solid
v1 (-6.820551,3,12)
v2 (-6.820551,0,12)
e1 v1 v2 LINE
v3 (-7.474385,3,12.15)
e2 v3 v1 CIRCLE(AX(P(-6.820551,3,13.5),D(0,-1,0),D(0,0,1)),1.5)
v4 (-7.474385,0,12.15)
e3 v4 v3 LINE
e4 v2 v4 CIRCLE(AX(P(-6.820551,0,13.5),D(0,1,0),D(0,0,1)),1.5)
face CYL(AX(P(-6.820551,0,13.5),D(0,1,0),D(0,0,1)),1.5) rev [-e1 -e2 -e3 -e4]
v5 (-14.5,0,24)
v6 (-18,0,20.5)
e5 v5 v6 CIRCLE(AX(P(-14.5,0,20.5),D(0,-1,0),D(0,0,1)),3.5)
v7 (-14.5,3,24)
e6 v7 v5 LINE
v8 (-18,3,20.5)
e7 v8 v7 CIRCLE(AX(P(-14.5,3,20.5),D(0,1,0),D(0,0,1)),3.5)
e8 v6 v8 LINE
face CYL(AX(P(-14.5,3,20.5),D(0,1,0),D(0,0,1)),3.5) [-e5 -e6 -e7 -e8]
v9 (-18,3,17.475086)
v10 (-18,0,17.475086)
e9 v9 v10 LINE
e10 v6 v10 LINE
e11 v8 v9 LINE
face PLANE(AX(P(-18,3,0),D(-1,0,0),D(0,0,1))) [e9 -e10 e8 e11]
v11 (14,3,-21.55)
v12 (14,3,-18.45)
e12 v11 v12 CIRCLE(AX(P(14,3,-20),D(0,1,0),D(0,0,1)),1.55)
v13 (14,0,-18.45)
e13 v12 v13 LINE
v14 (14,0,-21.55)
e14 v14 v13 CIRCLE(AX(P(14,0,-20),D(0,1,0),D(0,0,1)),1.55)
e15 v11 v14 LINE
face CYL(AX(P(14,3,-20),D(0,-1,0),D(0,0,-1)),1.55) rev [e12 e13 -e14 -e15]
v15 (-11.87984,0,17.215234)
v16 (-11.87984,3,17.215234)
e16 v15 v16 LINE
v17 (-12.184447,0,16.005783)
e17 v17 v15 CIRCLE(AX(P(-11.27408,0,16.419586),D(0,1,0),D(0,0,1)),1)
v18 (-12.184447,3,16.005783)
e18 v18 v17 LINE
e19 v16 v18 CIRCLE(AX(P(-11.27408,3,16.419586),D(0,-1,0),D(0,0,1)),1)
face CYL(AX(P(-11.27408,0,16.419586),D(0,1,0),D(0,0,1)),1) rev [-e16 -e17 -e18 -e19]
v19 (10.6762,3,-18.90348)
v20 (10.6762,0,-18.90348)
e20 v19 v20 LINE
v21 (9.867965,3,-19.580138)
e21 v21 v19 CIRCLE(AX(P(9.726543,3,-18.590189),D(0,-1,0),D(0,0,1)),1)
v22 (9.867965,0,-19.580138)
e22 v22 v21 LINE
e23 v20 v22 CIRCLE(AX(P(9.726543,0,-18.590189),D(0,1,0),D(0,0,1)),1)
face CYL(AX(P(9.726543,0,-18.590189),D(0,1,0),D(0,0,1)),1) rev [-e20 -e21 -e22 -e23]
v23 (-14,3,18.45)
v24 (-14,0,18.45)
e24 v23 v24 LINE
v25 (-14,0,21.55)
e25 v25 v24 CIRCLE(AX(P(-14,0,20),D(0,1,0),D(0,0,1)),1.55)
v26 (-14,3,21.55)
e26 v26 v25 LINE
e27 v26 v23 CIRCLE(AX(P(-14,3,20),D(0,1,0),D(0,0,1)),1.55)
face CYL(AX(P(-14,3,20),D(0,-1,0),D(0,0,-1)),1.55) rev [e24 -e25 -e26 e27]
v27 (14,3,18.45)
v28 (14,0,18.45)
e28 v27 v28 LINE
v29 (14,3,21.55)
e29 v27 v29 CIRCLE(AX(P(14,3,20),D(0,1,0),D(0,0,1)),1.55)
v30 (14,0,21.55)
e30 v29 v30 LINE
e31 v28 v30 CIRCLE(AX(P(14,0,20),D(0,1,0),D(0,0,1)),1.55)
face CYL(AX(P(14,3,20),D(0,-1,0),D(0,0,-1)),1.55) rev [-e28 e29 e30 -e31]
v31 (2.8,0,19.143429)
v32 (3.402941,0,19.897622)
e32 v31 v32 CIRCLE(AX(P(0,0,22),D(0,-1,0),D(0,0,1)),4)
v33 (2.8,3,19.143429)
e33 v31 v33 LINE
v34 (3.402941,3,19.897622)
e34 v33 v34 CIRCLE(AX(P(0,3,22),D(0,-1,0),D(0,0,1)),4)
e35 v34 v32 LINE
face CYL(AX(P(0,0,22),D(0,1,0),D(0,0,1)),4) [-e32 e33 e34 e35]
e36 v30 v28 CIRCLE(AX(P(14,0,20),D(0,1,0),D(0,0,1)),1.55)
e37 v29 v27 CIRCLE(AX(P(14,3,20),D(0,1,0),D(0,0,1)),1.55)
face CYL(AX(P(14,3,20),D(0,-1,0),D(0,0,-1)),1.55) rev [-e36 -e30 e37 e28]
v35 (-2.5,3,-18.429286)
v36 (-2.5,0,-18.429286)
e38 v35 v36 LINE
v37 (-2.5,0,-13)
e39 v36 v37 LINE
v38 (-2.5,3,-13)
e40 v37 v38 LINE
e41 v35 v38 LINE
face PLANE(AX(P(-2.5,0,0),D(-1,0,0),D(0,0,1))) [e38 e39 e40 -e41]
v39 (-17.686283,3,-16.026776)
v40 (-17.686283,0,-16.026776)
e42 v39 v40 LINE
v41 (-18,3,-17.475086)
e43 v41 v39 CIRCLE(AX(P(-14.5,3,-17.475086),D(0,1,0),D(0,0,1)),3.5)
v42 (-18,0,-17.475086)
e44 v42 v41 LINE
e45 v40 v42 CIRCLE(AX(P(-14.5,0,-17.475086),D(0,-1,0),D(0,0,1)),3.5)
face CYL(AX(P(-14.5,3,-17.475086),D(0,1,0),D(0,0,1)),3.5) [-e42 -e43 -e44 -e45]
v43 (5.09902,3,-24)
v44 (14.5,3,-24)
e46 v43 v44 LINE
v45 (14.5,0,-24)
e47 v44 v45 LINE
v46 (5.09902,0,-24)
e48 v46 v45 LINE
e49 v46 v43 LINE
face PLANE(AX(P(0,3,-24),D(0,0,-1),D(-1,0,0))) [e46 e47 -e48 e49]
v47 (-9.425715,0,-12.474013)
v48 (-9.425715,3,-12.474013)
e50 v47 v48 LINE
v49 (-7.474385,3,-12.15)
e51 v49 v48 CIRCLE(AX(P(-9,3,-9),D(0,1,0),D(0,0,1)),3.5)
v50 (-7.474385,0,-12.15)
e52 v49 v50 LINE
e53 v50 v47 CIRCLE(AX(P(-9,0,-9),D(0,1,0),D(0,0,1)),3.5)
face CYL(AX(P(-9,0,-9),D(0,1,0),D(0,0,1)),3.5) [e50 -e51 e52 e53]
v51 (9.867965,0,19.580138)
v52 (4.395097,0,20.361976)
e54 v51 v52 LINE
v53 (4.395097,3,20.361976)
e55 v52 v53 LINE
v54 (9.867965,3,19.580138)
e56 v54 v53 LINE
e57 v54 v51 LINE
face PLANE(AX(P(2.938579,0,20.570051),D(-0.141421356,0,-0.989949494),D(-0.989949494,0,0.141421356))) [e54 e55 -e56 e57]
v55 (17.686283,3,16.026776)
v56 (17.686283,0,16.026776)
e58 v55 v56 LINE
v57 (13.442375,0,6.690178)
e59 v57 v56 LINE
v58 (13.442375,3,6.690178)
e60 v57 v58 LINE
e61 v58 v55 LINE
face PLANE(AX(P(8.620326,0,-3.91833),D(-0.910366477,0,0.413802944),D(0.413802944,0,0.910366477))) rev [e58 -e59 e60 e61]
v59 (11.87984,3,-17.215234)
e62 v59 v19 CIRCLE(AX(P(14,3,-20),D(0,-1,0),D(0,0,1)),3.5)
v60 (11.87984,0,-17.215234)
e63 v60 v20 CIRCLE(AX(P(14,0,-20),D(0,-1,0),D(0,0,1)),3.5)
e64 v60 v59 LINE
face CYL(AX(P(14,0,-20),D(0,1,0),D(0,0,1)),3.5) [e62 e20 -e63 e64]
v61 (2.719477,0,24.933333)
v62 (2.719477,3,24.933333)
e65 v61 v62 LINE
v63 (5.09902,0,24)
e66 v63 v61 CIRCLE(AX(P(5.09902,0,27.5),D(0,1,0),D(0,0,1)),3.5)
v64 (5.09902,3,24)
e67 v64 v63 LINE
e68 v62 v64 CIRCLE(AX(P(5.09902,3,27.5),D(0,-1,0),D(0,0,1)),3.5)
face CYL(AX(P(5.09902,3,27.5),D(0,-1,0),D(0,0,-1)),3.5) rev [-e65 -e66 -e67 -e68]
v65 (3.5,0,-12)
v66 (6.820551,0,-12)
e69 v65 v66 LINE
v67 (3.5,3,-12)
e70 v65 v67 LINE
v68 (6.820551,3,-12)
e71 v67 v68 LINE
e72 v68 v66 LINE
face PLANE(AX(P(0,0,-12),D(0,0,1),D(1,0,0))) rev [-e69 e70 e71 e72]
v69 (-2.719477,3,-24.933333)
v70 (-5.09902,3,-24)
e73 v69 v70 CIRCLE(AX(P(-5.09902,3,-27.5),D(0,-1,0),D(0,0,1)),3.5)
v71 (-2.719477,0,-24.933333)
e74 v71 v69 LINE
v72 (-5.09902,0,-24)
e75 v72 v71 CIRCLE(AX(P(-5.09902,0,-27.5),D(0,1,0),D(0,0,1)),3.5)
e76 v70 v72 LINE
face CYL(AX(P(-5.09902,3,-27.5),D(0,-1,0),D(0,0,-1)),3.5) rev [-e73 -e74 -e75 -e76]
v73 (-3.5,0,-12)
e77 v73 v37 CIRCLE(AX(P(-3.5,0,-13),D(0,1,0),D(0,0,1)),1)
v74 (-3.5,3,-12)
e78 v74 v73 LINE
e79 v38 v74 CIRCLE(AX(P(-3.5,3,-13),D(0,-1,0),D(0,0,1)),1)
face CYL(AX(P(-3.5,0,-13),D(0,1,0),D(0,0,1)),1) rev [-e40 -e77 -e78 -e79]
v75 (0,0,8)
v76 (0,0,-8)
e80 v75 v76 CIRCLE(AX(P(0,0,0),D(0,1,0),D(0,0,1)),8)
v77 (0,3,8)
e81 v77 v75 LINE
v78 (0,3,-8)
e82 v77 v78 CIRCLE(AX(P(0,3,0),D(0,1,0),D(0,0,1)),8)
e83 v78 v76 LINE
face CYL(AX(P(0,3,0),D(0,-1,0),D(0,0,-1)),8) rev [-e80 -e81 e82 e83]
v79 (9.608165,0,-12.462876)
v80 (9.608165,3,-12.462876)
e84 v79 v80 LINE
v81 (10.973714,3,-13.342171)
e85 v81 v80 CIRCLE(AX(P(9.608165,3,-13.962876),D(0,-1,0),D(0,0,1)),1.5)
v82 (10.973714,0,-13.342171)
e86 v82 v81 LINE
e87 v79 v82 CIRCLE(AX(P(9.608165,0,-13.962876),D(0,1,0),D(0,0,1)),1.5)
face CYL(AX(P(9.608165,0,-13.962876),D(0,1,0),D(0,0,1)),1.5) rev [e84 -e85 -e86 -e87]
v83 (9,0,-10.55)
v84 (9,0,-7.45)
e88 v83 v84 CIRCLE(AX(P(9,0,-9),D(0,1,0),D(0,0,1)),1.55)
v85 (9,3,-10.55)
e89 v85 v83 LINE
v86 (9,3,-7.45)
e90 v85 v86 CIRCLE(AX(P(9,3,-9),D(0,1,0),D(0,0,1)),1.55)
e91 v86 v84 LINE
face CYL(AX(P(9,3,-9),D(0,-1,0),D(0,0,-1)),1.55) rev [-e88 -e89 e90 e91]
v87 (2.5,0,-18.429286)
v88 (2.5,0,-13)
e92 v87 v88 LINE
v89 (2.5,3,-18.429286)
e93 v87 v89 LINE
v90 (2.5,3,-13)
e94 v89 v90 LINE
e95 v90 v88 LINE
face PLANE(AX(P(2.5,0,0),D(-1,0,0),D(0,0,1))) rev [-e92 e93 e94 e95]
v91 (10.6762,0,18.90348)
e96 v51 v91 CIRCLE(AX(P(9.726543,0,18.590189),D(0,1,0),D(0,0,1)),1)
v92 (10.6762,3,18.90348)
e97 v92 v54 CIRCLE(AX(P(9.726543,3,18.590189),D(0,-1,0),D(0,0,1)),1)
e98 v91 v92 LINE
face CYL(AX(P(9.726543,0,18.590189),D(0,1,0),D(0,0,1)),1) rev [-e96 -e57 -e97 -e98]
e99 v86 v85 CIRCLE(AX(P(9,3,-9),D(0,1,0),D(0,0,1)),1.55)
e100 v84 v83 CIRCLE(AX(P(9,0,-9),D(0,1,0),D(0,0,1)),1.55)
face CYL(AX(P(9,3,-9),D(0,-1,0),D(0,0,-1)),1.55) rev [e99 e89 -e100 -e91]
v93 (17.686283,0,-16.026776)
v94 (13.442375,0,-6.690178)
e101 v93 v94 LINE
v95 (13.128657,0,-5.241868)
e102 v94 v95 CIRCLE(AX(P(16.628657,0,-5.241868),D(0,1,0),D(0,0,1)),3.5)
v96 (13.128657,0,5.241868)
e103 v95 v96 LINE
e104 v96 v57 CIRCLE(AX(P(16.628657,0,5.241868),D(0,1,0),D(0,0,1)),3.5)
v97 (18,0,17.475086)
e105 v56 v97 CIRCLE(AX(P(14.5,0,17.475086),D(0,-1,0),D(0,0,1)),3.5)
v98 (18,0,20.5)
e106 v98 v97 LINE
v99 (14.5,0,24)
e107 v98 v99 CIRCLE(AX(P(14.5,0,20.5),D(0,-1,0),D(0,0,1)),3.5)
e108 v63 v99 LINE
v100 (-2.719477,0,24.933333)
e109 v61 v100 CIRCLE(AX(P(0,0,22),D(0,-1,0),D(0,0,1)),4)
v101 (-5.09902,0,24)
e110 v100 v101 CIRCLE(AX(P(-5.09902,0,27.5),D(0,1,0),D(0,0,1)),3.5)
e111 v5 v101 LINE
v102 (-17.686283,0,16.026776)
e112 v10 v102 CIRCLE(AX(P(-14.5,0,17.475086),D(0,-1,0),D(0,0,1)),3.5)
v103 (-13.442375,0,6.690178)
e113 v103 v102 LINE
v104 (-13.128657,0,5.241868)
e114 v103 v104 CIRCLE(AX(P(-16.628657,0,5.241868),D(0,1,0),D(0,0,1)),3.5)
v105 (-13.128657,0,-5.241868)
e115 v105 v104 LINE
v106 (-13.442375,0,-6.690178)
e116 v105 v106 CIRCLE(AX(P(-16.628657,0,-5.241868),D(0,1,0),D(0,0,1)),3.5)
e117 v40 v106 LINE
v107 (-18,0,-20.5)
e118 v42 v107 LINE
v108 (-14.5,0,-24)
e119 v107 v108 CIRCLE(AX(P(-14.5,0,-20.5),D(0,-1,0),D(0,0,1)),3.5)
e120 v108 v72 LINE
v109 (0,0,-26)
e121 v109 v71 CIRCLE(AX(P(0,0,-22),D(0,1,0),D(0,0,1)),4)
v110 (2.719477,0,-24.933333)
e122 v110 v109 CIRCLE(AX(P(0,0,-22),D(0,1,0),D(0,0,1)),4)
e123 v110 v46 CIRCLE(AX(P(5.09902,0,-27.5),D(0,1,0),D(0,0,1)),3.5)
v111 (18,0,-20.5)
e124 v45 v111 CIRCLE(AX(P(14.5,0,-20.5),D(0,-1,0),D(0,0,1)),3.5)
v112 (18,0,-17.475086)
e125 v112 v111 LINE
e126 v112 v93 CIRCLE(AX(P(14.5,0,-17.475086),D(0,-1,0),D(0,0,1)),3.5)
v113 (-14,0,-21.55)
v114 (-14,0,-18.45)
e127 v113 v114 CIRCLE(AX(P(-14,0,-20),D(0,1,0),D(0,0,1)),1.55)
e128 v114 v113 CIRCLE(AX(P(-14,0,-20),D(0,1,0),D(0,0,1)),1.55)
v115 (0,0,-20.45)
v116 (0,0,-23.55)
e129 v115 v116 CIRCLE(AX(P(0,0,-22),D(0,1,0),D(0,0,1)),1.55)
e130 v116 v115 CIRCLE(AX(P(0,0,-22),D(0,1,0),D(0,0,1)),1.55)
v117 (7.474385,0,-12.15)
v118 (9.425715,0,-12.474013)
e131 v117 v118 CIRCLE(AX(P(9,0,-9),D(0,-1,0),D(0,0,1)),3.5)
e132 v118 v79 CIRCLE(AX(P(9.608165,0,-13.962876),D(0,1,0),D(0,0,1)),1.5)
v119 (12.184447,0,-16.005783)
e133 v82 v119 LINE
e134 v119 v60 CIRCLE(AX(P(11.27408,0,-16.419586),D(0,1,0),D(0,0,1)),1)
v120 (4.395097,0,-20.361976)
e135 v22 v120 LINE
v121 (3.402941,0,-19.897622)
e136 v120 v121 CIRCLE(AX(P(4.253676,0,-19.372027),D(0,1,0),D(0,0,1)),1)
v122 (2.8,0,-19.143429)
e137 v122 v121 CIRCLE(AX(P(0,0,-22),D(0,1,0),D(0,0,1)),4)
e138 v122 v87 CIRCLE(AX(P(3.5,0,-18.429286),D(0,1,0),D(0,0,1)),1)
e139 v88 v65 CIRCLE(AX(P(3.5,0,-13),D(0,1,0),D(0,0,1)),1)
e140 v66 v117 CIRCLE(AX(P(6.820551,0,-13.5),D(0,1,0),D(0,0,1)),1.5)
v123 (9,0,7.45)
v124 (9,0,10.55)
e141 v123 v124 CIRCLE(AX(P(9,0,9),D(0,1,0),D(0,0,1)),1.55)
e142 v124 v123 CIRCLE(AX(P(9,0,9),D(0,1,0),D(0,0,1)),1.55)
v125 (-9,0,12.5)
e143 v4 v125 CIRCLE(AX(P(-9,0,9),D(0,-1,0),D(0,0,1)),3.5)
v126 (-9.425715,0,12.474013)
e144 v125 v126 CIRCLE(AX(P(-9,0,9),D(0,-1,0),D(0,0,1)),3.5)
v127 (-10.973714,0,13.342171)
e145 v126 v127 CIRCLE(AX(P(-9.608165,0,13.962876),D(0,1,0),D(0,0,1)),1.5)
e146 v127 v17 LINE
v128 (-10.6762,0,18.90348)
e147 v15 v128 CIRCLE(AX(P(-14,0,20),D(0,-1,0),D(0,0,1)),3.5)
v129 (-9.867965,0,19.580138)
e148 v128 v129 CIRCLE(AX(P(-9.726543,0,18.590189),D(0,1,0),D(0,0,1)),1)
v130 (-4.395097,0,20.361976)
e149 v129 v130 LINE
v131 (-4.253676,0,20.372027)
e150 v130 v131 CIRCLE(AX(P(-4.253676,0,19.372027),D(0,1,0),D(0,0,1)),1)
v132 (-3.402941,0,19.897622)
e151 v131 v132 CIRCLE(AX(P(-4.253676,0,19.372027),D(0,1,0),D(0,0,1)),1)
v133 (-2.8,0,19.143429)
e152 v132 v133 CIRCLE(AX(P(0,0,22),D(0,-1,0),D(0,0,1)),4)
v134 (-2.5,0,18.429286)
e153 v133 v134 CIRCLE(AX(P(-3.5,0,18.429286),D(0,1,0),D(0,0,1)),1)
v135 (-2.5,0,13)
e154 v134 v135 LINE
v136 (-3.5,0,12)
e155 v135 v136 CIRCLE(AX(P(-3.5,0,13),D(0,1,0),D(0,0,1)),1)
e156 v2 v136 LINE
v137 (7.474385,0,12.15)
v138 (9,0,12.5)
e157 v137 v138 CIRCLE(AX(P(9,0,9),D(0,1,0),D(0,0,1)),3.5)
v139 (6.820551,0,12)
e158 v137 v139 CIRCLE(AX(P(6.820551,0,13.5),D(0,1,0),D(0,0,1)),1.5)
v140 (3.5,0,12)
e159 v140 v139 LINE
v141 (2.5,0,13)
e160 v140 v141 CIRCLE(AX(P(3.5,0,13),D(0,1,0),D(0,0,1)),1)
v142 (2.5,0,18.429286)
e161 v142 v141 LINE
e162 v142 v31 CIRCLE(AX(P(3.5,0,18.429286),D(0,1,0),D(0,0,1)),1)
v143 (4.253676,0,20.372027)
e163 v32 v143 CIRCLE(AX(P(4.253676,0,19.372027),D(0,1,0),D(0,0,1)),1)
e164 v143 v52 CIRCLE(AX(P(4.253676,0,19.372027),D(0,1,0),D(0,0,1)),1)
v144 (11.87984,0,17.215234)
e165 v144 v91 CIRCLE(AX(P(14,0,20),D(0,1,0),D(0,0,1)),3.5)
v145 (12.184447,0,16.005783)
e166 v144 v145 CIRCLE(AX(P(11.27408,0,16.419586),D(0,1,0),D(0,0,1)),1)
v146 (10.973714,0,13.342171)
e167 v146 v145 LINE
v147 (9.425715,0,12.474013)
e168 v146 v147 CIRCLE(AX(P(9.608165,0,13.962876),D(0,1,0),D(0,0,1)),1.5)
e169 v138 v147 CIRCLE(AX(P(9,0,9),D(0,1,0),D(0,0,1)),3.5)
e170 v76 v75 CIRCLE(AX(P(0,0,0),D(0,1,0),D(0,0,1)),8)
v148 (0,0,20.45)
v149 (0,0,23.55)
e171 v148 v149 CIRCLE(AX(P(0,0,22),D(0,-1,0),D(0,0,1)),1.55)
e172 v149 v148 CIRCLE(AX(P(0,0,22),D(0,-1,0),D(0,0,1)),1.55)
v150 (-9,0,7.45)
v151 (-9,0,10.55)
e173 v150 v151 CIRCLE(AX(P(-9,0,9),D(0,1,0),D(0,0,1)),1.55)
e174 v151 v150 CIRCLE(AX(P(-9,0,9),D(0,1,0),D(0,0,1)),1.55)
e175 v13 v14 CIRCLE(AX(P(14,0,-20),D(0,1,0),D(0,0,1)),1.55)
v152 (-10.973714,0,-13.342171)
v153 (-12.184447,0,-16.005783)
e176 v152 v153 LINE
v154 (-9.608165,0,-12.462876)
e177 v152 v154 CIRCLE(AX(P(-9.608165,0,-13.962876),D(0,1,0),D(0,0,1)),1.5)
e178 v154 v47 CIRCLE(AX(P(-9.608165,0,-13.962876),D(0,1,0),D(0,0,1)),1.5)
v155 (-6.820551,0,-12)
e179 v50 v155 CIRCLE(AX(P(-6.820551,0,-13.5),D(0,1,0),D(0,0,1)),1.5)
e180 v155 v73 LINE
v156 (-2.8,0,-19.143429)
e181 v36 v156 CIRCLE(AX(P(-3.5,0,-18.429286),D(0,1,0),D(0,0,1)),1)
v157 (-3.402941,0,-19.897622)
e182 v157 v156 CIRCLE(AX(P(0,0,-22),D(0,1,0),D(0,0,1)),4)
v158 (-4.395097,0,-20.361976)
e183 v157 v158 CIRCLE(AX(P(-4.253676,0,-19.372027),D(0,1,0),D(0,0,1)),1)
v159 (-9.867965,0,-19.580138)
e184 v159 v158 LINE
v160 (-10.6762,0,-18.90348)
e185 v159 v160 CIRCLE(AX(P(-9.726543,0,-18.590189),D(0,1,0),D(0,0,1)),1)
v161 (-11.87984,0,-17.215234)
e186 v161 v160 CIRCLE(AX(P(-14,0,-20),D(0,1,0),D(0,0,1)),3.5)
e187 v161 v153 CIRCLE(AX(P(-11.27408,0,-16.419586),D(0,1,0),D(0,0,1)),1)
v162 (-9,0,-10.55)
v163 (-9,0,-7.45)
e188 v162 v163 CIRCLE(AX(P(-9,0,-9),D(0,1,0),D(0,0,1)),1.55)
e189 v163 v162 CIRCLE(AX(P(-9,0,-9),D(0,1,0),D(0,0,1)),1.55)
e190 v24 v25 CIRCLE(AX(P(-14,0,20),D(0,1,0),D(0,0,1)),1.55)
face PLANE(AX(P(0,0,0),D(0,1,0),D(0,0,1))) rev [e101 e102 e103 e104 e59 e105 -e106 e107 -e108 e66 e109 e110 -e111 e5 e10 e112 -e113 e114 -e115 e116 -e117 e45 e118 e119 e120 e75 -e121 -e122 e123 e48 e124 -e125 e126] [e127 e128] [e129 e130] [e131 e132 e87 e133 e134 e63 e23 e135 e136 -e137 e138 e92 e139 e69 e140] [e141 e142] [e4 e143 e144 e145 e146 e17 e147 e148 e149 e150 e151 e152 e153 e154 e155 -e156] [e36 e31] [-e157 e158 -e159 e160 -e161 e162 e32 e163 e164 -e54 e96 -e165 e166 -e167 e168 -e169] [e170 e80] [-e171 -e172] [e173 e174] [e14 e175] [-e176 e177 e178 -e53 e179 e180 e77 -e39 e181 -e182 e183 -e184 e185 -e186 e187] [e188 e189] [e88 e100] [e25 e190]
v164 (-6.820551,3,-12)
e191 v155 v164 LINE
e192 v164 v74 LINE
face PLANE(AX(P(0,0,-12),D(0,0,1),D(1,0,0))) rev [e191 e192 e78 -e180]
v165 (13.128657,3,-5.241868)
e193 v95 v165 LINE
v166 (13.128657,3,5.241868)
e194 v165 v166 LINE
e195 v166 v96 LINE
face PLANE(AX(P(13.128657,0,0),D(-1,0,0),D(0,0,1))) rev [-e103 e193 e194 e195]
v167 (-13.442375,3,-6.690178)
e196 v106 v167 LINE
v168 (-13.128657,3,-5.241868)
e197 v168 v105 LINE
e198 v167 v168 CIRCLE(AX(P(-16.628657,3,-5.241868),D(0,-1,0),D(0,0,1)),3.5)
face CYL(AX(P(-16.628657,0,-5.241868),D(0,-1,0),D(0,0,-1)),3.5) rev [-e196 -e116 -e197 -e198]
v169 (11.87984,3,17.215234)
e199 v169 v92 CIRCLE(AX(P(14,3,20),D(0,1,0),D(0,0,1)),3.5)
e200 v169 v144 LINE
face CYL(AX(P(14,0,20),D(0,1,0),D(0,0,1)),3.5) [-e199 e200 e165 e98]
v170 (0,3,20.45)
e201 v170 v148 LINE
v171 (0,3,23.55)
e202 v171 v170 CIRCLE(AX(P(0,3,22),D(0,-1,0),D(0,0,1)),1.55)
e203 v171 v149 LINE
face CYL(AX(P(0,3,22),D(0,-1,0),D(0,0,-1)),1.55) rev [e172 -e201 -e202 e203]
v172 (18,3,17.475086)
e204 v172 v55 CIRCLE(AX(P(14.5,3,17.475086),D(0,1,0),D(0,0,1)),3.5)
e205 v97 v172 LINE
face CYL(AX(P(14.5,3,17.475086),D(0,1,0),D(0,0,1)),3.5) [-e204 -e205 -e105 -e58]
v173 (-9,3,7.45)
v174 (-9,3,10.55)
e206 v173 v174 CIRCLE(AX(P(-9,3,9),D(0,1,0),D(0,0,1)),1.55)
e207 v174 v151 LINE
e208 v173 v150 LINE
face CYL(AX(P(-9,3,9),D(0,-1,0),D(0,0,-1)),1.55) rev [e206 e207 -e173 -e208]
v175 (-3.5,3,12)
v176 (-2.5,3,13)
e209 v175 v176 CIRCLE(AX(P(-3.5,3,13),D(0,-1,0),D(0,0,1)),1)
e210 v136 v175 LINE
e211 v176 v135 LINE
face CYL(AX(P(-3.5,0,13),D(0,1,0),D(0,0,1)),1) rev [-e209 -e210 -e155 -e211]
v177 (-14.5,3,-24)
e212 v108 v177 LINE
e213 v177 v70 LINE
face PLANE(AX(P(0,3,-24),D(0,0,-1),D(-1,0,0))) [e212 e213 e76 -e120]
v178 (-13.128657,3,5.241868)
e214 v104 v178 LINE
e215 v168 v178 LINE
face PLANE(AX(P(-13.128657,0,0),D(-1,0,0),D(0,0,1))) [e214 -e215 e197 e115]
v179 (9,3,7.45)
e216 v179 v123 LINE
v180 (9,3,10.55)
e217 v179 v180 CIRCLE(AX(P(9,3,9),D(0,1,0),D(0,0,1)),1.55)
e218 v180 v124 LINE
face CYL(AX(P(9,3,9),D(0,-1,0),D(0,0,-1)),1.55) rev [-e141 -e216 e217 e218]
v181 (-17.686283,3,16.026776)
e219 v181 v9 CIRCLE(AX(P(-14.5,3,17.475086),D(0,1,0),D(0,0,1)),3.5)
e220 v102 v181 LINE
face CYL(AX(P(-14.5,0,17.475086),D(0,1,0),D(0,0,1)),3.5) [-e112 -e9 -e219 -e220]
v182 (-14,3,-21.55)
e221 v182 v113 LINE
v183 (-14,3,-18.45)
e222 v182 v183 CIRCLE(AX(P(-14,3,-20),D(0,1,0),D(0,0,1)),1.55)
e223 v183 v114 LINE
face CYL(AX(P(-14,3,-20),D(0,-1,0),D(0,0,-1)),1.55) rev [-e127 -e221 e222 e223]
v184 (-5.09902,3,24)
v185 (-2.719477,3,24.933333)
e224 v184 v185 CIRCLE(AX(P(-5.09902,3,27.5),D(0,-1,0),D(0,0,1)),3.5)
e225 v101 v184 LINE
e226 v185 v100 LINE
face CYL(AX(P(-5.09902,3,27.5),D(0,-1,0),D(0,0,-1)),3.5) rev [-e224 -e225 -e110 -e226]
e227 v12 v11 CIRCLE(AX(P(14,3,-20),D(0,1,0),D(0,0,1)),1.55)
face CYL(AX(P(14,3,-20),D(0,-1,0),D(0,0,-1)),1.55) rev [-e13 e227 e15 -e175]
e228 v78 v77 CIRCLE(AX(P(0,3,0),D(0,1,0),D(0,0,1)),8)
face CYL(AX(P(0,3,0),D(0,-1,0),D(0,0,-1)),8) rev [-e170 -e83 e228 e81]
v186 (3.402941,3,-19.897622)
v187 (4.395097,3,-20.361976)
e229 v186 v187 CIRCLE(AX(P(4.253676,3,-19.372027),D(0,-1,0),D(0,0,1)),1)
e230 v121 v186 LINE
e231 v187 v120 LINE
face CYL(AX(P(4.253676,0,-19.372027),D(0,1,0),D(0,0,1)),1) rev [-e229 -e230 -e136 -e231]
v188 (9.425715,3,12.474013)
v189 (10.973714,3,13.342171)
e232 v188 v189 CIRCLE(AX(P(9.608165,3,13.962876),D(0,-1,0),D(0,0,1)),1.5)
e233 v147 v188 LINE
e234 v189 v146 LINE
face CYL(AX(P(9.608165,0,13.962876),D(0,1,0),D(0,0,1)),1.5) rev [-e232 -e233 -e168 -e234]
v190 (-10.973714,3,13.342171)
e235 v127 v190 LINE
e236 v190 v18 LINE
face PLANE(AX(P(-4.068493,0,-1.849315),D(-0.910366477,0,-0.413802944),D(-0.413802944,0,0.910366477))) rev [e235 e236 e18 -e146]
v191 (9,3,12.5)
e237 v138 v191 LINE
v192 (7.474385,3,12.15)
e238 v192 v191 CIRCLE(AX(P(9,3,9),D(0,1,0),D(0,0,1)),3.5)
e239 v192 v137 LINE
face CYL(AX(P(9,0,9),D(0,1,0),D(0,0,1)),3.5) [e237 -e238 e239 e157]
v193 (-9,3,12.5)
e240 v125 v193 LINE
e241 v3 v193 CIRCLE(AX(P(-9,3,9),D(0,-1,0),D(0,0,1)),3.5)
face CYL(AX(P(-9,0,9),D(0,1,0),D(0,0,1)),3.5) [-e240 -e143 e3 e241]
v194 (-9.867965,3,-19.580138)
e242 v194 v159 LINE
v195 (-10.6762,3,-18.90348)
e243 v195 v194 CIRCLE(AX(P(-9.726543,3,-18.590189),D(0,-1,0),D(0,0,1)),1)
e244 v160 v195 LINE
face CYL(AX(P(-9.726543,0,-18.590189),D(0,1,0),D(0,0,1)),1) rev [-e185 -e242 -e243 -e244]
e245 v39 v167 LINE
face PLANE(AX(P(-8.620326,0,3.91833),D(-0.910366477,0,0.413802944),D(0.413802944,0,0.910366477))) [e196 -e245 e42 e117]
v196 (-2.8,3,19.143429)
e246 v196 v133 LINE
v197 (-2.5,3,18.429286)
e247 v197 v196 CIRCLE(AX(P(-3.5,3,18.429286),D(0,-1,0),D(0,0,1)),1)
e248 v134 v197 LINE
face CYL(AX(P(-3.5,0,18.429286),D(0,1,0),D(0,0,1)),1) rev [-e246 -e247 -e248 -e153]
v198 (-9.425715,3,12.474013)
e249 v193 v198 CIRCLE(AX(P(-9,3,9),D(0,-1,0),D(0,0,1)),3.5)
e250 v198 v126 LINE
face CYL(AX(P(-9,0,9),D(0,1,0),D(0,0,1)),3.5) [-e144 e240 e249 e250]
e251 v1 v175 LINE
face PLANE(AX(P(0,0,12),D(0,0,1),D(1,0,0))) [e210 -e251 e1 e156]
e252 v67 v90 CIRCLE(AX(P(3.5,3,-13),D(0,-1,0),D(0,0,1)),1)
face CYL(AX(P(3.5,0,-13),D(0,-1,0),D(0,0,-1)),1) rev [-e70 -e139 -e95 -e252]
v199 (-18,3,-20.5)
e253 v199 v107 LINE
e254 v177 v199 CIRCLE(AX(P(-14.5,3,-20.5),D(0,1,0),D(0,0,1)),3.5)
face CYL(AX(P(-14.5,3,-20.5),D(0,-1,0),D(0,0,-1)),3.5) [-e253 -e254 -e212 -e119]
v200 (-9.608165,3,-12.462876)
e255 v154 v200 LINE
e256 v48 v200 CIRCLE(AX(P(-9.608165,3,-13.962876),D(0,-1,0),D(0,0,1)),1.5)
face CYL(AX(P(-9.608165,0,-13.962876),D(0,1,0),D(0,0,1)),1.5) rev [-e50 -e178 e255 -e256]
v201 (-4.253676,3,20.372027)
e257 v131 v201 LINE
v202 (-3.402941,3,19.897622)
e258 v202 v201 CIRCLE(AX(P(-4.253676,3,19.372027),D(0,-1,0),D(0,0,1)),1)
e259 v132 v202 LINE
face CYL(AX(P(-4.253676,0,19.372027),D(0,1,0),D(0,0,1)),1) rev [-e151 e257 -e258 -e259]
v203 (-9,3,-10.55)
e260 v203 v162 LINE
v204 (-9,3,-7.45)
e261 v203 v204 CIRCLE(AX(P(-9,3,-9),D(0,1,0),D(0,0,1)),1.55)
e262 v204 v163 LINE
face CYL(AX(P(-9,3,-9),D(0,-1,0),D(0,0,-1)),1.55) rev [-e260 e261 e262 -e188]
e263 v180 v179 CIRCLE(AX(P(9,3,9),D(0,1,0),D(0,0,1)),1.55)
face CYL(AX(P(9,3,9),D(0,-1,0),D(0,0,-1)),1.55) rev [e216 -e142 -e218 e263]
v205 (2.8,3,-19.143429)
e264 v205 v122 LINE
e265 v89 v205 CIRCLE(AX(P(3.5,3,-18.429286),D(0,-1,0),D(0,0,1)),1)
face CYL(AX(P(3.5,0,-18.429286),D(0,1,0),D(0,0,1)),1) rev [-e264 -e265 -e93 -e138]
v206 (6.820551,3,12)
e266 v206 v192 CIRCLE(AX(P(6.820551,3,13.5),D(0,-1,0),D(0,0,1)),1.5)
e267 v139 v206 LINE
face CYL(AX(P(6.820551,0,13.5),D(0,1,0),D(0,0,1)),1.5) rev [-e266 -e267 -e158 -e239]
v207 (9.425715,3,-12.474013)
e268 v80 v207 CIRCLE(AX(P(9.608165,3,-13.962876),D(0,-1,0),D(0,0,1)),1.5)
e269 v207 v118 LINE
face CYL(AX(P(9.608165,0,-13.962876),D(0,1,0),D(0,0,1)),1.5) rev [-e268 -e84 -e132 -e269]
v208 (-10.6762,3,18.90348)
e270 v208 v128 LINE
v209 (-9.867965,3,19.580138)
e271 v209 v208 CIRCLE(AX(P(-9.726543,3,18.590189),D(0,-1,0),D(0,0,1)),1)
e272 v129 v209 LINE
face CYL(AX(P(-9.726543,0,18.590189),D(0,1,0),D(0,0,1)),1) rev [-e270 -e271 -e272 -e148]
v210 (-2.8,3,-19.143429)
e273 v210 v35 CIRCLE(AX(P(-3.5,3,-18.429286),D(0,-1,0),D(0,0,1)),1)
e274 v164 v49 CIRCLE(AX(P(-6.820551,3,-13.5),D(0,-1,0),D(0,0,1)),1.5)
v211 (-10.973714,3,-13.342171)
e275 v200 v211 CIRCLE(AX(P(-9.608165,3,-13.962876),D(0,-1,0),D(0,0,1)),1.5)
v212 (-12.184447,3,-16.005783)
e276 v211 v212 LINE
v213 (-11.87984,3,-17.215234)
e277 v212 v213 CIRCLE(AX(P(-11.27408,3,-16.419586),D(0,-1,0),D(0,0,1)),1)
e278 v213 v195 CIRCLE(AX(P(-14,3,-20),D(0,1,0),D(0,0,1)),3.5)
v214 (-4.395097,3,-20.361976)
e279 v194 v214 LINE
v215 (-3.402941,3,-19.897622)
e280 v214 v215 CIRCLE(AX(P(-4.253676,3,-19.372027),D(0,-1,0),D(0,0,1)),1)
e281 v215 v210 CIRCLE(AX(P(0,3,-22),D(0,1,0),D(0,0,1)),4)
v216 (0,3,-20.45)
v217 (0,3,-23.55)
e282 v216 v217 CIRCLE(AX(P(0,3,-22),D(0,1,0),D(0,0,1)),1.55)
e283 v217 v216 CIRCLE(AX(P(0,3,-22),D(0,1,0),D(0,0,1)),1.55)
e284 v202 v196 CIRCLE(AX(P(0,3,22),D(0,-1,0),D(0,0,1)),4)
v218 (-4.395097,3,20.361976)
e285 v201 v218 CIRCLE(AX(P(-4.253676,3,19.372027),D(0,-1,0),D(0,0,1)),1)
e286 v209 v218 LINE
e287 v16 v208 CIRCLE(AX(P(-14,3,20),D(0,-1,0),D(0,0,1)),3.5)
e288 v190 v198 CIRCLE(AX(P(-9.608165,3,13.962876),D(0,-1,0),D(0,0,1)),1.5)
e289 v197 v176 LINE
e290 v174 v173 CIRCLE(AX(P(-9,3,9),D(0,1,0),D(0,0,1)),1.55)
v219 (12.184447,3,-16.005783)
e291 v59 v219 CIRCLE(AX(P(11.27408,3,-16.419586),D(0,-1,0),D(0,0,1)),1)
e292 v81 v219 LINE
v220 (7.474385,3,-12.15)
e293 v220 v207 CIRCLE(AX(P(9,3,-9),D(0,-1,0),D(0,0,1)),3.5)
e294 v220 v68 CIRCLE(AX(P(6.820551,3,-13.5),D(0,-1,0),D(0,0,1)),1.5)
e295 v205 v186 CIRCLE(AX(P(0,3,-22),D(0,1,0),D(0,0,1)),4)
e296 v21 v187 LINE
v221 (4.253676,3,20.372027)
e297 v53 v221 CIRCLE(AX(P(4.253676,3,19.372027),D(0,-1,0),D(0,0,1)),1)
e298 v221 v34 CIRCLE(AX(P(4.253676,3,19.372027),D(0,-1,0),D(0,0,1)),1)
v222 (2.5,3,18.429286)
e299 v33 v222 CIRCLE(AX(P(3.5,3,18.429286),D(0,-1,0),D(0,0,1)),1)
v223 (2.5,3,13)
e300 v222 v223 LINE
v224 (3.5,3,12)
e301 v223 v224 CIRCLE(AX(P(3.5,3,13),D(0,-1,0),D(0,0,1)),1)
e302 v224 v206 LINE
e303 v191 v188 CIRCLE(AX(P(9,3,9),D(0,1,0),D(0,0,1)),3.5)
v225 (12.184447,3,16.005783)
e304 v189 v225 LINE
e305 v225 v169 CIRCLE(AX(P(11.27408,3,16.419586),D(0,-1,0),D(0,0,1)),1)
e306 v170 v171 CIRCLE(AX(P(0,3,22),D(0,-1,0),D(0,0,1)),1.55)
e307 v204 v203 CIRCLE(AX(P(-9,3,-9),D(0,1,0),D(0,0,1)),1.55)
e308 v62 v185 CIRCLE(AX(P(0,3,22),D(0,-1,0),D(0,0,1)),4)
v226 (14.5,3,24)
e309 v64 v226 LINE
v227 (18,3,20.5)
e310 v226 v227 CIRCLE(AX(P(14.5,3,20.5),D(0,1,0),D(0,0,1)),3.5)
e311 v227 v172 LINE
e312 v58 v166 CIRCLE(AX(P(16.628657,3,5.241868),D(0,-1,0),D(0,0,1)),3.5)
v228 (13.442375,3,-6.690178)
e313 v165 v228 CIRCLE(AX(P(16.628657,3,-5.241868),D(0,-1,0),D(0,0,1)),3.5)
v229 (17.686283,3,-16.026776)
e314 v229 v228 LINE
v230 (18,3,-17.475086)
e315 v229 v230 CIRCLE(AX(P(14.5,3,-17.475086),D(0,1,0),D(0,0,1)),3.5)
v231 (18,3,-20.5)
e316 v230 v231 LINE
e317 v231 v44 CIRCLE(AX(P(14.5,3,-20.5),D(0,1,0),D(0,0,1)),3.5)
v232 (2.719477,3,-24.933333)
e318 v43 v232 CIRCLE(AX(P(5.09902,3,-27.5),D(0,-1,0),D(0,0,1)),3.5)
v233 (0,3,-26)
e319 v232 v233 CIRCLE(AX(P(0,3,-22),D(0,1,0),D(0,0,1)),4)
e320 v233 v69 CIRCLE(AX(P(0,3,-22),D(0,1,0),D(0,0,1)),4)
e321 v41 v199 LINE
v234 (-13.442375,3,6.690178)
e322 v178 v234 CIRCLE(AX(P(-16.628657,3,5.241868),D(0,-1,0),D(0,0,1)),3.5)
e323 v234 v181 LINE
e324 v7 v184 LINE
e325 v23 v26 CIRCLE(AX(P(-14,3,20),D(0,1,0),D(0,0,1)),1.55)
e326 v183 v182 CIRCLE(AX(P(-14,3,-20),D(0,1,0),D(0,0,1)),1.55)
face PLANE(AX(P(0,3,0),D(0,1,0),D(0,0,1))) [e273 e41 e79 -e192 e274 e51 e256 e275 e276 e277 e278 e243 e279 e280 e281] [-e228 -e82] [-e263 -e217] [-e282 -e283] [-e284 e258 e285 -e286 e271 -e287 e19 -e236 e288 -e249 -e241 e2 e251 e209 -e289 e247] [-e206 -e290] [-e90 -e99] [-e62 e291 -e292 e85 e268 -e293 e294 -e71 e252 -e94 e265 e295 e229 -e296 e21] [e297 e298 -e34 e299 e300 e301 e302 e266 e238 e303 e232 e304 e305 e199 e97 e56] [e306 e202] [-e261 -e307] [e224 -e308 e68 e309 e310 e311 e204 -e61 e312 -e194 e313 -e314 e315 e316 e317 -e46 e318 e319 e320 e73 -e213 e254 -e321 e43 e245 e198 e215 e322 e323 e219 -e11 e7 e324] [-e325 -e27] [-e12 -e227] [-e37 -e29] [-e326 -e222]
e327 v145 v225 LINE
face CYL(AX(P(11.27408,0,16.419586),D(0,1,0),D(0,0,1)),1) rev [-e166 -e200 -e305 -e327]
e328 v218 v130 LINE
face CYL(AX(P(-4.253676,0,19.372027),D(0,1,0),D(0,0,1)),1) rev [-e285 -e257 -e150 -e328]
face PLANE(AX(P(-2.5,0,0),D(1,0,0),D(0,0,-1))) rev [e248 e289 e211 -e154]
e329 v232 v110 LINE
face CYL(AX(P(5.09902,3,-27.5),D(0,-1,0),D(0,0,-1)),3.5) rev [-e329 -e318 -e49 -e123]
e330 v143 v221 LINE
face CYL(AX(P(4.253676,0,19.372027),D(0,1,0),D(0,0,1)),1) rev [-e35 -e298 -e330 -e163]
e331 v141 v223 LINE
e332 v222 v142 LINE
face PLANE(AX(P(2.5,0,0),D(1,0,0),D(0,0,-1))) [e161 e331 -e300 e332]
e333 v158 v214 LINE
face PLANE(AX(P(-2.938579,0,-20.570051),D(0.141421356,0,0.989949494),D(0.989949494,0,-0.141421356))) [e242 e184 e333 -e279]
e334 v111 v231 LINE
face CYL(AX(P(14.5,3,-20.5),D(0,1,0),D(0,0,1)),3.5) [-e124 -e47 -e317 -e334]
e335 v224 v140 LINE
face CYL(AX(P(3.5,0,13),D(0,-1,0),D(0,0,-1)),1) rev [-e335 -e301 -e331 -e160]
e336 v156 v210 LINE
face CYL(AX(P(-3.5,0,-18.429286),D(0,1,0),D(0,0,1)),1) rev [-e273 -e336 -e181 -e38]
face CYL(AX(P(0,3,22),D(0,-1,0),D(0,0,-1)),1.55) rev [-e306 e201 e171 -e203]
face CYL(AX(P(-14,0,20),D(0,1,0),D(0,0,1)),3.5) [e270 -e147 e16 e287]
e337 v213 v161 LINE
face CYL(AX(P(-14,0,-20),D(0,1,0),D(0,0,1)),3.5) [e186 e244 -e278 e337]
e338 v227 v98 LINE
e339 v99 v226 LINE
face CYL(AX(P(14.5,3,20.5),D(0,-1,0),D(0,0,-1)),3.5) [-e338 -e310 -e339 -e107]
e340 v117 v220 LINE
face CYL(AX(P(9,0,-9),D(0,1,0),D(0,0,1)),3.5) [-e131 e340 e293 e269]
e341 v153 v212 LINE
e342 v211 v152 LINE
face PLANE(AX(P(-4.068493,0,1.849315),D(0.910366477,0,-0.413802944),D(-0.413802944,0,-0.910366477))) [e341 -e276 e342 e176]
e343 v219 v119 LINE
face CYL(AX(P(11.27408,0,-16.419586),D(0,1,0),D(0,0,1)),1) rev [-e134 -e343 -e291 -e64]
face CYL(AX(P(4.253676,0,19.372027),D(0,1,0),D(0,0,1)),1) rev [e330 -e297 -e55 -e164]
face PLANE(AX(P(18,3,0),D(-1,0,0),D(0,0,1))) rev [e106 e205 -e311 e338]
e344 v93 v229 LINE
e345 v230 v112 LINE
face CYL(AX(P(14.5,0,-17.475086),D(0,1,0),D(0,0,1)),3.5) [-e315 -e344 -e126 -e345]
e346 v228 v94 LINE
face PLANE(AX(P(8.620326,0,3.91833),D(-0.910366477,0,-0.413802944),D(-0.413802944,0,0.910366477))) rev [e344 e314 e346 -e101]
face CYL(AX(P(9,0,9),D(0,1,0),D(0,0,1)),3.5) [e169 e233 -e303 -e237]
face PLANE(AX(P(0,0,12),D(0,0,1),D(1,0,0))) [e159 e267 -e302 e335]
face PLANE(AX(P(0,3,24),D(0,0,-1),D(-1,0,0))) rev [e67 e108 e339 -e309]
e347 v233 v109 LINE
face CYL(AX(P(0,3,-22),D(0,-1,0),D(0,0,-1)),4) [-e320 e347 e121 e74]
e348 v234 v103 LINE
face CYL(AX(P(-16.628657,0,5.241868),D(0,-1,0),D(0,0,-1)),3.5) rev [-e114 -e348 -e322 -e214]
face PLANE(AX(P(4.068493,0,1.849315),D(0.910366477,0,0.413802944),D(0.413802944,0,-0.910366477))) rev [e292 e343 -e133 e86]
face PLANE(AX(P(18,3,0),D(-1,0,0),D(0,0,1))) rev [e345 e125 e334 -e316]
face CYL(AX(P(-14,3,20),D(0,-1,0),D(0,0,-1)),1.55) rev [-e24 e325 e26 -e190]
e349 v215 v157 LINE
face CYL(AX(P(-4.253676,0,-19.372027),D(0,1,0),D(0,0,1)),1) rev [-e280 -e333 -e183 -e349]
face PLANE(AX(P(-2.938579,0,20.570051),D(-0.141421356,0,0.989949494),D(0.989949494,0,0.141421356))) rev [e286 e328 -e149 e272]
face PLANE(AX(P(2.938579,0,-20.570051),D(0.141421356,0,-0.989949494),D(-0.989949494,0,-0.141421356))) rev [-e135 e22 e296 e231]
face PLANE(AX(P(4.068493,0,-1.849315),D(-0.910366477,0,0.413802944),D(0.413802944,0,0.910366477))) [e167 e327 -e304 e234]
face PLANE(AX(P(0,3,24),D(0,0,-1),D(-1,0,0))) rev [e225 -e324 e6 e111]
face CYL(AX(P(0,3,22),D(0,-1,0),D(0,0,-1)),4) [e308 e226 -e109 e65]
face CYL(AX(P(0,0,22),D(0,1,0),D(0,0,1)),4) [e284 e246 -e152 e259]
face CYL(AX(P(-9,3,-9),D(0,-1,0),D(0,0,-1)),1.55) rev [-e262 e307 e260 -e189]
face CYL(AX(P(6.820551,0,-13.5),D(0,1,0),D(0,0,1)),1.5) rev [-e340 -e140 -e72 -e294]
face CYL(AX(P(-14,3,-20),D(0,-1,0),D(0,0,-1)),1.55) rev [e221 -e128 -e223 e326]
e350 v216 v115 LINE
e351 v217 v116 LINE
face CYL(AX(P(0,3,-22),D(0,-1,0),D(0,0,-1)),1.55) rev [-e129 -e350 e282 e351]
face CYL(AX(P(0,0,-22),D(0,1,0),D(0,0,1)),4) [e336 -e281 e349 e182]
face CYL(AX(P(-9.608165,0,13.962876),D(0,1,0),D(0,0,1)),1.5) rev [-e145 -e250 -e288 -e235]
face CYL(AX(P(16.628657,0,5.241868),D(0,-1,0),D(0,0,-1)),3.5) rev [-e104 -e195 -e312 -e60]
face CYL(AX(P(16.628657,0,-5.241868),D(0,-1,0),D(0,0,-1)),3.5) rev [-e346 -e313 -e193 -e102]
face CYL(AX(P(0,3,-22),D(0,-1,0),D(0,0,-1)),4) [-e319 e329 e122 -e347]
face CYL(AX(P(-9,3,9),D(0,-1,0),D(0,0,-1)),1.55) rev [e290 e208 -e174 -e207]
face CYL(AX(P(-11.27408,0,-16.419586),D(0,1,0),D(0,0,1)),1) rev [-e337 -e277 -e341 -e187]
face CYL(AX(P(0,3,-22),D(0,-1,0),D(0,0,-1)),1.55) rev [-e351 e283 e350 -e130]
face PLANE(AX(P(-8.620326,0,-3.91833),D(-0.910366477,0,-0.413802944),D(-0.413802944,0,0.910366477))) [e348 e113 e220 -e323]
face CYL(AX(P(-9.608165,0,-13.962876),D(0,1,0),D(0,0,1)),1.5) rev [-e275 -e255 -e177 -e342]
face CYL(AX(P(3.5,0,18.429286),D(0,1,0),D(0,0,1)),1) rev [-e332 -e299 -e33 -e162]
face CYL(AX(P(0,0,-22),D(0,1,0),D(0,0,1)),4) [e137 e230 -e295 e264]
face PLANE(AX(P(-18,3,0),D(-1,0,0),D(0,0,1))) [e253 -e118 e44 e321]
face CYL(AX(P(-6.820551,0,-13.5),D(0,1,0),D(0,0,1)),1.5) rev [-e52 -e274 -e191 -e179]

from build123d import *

# Parameters (mm, degrees)
SKETCH_3_R               = 1.55
SKETCH_3_R_2             = 8
EXTRUDE_1_DEPTH          = 3
CUT_EXTRUDE_1_DEPTH      = 32.764760349
CUT_EXTRUDE_1_DEPTH_BACK = 32.764760349
FILLET_1_R               = 3.5
FILLET_6_R               = 1
FILLET_7_R               = 1.5


with BuildPart() as part:
    # 草图3 → 凸台-拉伸1 (new body)
    # profile 1 of 7: a face of its own
    with BuildSketch(Plane(origin=(0, 0, 0), x_dir=(1, 0, 0), z_dir=(0, 1, 0))):
        with BuildLine():
            Line((-18, 24), (-18, -24))
            Line((-18, -24), (-3.464101615, -24))
            ThreePointArc((-3.464101615, -24), (-1.03527618, -18.136296695), (4, -22))
            ThreePointArc((4, -22), (3.863703305, -23.03527618), (3.464101615, -24))
            Line((3.464101615, -24), (18, -24))
            Line((18, -24), (18, 24))
            Line((18, 24), (3.464101615, 24))
            ThreePointArc((3.464101615, 24), (3.863703305, 23.03527618), (4, 22))
            ThreePointArc((4, 22), (-1.03527618, 18.136296695), (-3.464101615, 24))
            Line((-3.464101615, 24), (-18, 24))
        make_face()
        with Locations(Location((-14, -20, 0), (0, 0, 270))):
            Circle(SKETCH_3_R, mode=Mode.SUBTRACT)
        with Locations(Location((-9, -9, 0), (0, 0, 270))):
            Circle(SKETCH_3_R, mode=Mode.SUBTRACT)
        with Locations(Location((14, -20, 0), (0, 0, 270))):
            Circle(SKETCH_3_R, mode=Mode.SUBTRACT)
        with Locations(Location((9, -9, 0), (0, 0, 270))):
            Circle(SKETCH_3_R, mode=Mode.SUBTRACT)
        with Locations(Location((-9, 9, 0), (0, 0, 270))):
            Circle(SKETCH_3_R, mode=Mode.SUBTRACT)
        with Locations(Location((0, 0, 0), (0, 0, 270))):
            Circle(SKETCH_3_R_2, mode=Mode.SUBTRACT)
        with Locations(Location((-14, 20, 0), (0, 0, 270))):
            Circle(SKETCH_3_R, mode=Mode.SUBTRACT)
        with Locations(Location((9, 9, 0), (0, 0, 270))):
            Circle(SKETCH_3_R, mode=Mode.SUBTRACT)
        with Locations(Location((14, 20, 0), (0, 0, 270))):
            Circle(SKETCH_3_R, mode=Mode.SUBTRACT)
    # profile 2 of 7: a face of its own
    with BuildSketch(Plane(origin=(0, 0, 0), x_dir=(1, 0, 0), z_dir=(0, 1, 0))):
        with BuildLine():
            Line((-18, 24), (-18, -24))
            Line((-18, -24), (-3.464101615, -24))
            ThreePointArc((-3.464101615, -24), (-1.03527618, -18.136296695), (4, -22))
            ThreePointArc((4, -22), (3.863703305, -23.03527618), (3.464101615, -24))
            Line((3.464101615, -24), (18, -24))
            Line((18, -24), (18, 24))
            Line((18, 24), (3.464101615, 24))
            ThreePointArc((3.464101615, 24), (3.863703305, 23.03527618), (4, 22))
            ThreePointArc((4, 22), (-1.03527618, 18.136296695), (-3.464101615, 24))
            Line((-3.464101615, 24), (-18, 24))
        make_face()
        with Locations(Location((-14, -20, 0), (0, 0, 270))):
            Circle(SKETCH_3_R, mode=Mode.SUBTRACT)
        with Locations(Location((-9, -9, 0), (0, 0, 270))):
            Circle(SKETCH_3_R, mode=Mode.SUBTRACT)
        with Locations(Location((14, -20, 0), (0, 0, 270))):
            Circle(SKETCH_3_R, mode=Mode.SUBTRACT)
        with Locations(Location((9, -9, 0), (0, 0, 270))):
            Circle(SKETCH_3_R, mode=Mode.SUBTRACT)
        with Locations(Location((-9, 9, 0), (0, 0, 270))):
            Circle(SKETCH_3_R, mode=Mode.SUBTRACT)
        with Locations(Location((0, 0, 0), (0, 0, 270))):
            Circle(SKETCH_3_R_2, mode=Mode.SUBTRACT)
        with Locations(Location((-14, 20, 0), (0, 0, 270))):
            Circle(SKETCH_3_R, mode=Mode.SUBTRACT)
        with Locations(Location((9, 9, 0), (0, 0, 270))):
            Circle(SKETCH_3_R, mode=Mode.SUBTRACT)
        with Locations(Location((14, 20, 0), (0, 0, 270))):
            Circle(SKETCH_3_R, mode=Mode.SUBTRACT)
    # profile 3 of 7: a face of its own
    with BuildSketch(Plane(origin=(0, 0, 0), x_dir=(1, 0, 0), z_dir=(0, 1, 0))):
        with BuildLine():
            Line((-18, 24), (-18, -24))
            Line((-18, -24), (-3.464101615, -24))
            ThreePointArc((-3.464101615, -24), (-1.03527618, -18.136296695), (4, -22))
            ThreePointArc((4, -22), (3.863703305, -23.03527618), (3.464101615, -24))
            Line((3.464101615, -24), (18, -24))
            Line((18, -24), (18, 24))
            Line((18, 24), (3.464101615, 24))
            ThreePointArc((3.464101615, 24), (3.863703305, 23.03527618), (4, 22))
            ThreePointArc((4, 22), (-1.03527618, 18.136296695), (-3.464101615, 24))
            Line((-3.464101615, 24), (-18, 24))
        make_face()
        with Locations(Location((-14, -20, 0), (0, 0, 270))):
            Circle(SKETCH_3_R, mode=Mode.SUBTRACT)
        with Locations(Location((-9, -9, 0), (0, 0, 270))):
            Circle(SKETCH_3_R, mode=Mode.SUBTRACT)
        with Locations(Location((14, -20, 0), (0, 0, 270))):
            Circle(SKETCH_3_R, mode=Mode.SUBTRACT)
        with Locations(Location((9, -9, 0), (0, 0, 270))):
            Circle(SKETCH_3_R, mode=Mode.SUBTRACT)
        with Locations(Location((-9, 9, 0), (0, 0, 270))):
            Circle(SKETCH_3_R, mode=Mode.SUBTRACT)
        with Locations(Location((0, 0, 0), (0, 0, 270))):
            Circle(SKETCH_3_R_2, mode=Mode.SUBTRACT)
        with Locations(Location((-14, 20, 0), (0, 0, 270))):
            Circle(SKETCH_3_R, mode=Mode.SUBTRACT)
        with Locations(Location((9, 9, 0), (0, 0, 270))):
            Circle(SKETCH_3_R, mode=Mode.SUBTRACT)
        with Locations(Location((14, 20, 0), (0, 0, 270))):
            Circle(SKETCH_3_R, mode=Mode.SUBTRACT)
    # profile 4 of 7: a face of its own
    with BuildSketch(Plane(origin=(0, 0, 0), x_dir=(1, 0, 0), z_dir=(0, 1, 0))):
        with BuildLine():
            Line((3.464101615, 24), (-3.464101615, 24))
            ThreePointArc((-3.464101615, 24), (-1.03527618, 18.136296695), (4, 22))
            ThreePointArc((4, 22), (3.863703305, 23.03527618), (3.464101615, 24))
        make_face()
        with Locations(Location((0, 22, 0), (0, 0, 270))):
            Circle(SKETCH_3_R, mode=Mode.SUBTRACT)
    # profile 5 of 7: a face of its own
    with BuildSketch(Plane(origin=(0, 0, 0), x_dir=(1, 0, 0), z_dir=(0, 1, 0))):
        with BuildLine():
            ThreePointArc((3.464101615, 24), (0, 26), (-3.464101615, 24))
            Line((-3.464101615, 24), (3.464101615, 24))
        make_face()
    # profile 6 of 7: a face of its own
    with BuildSketch(Plane(origin=(0, 0, 0), x_dir=(1, 0, 0), z_dir=(0, 1, 0))):
        with BuildLine():
            Line((3.464101615, -24), (-3.464101615, -24))
            ThreePointArc((-3.464101615, -24), (0, -26), (3.464101615, -24))
        make_face()
    # profile 7 of 7: a face of its own
    with BuildSketch(Plane(origin=(0, 0, 0), x_dir=(1, 0, 0), z_dir=(0, 1, 0))):
        with BuildLine():
            ThreePointArc((4, -22), (-1.03527618, -18.136296695), (-3.464101615, -24))
            Line((-3.464101615, -24), (3.464101615, -24))
            ThreePointArc((3.464101615, -24), (3.863703305, -23.03527618), (4, -22))
        make_face()
        with Locations(Location((0, -22, 0), (0, 0, 270))):
            Circle(SKETCH_3_R, mode=Mode.SUBTRACT)
    extrude(amount=EXTRUDE_1_DEPTH)

    # 草图4 → 切除-拉伸1 (cut, two sides: drawn at the far end of the back side and taken through both)
    with BuildSketch(Plane(origin=(0, 3, 0), x_dir=(1, 0, 0), z_dir=(0, 1, 0)).offset(-CUT_EXTRUDE_1_DEPTH_BACK)):
        with BuildLine():
            Line((-12.551689695, 16.813717329), (-10.448310305, 12.186282671))
            ThreePointArc((-10.448310305, 12.186282671), (-8.799783301, 12.494268632), (-7.197224362, 12))
            Line((-7.197224362, 12), (-2.5, 12))
            Line((-2.5, 12), (-2.5, 18.877501001))
            ThreePointArc((-2.5, 18.877501001), (-3.19610794, 19.594819334), (-3.692636546, 20.462327949))
            Line((-3.692636546, 20.462327949), (-10.538187101, 19.484392155))
            ThreePointArc((-10.538187101, 19.484392155), (-11.205281145, 17.892976858), (-12.551689695, 16.813717329))
        make_face()
        with BuildLine():
            Line((2.5, 18.877501001), (2.5, 12))
            Line((2.5, 12), (7.197224362, 12))
            ThreePointArc((7.197224362, 12), (8.799783301, 12.494268632), (10.448310305, 12.186282671))
            Line((10.448310305, 12.186282671), (12.551689695, 16.813717329))
            ThreePointArc((12.551689695, 16.813717329), (11.205281145, 17.892976858), (10.538187101, 19.484392155))
            Line((10.538187101, 19.484392155), (3.692636546, 20.462327949))
            ThreePointArc((3.692636546, 20.462327949), (3.19610794, 19.594819334), (2.5, 18.877501001))
        make_face()
        Polygon((-13.128657261, 6), (-18, 16.716954026), (-18, -16.716954026), (-13.128657261, -6), align=None)
        Polygon((18, -16.716954026), (18, 16.716954026), (13.128657261, 6), (13.128657261, -6), align=None)
        with BuildLine():
            Line((-10.538187101, -19.484392155), (-3.692636546, -20.462327949))
            ThreePointArc((-3.692636546, -20.462327949), (-3.19610794, -19.594819334), (-2.5, -18.877501001))
            Line((-2.5, -18.877501001), (-2.5, -12))
            Line((-2.5, -12), (-7.197224362, -12))
            ThreePointArc((-7.197224362, -12), (-8.799783301, -12.494268632), (-10.448310305, -12.186282671))
            Line((-10.448310305, -12.186282671), (-12.551689695, -16.813717329))
            ThreePointArc((-12.551689695, -16.813717329), (-11.205281145, -17.892976858), (-10.538187101, -19.484392155))
        make_face()
        with BuildLine():
            ThreePointArc((2.5, -18.877501001), (3.19610794, -19.594819334), (3.692636546, -20.462327949))
            Line((3.692636546, -20.462327949), (10.538187101, -19.484392155))
            ThreePointArc((10.538187101, -19.484392155), (11.205281145, -17.892976858), (12.551689695, -16.813717329))
            Line((12.551689695, -16.813717329), (10.448310305, -12.186282671))
            ThreePointArc((10.448310305, -12.186282671), (8.799783301, -12.494268632), (7.197224362, -12))
            Line((7.197224362, -12), (2.5, -12))
            Line((2.5, -12), (2.5, -18.877501001))
        make_face()
    extrude(amount=CUT_EXTRUDE_1_DEPTH + CUT_EXTRUDE_1_DEPTH_BACK, mode=Mode.SUBTRACT)

    # 圆角1
    fillet_1_edges = [part.edges().sort_by_distance(p)[0] for p in [
        (13.128657261, 1.5, 6),
        (13.128657261, 1.5, -6),
        (18, 1.5, -16.716954026),
        (18, 1.5, 16.716954026),
        (-18, 1.5, -16.716954026),
        (-13.128657261, 1.5, -6),
        (-13.128657261, 1.5, 6),
        (-18, 1.5, 16.716954026),
        (-18, 1.5, 24),
        (-18, 1.5, -24),
        (-3.464101615, 1.5, -24),
        (3.464101615, 1.5, -24),
        (18, 1.5, -24),
        (18, 1.5, 24),
        (3.464101615, 1.5, 24),
        (-3.464101615, 1.5, 24),
    ]]
    fillet(fillet_1_edges, radius=FILLET_1_R)

    # 圆角6
    fillet_6_edges = [part.edges().sort_by_distance(p)[0] for p in [
        (-12.551689695, 1.5, 16.813717329),
        (-2.5, 1.5, 12),
        (-2.5, 1.5, 18.877501001),
        (-3.692636546, 1.5, 20.462327949),
        (-10.538187101, 1.5, 19.484392155),
        (12.551689695, 1.5, -16.813717329),
        (2.5, 1.5, -12),
        (2.5, 1.5, -18.877501001),
        (3.692636546, 1.5, -20.462327949),
        (10.538187101, 1.5, -19.484392155),
        (2.5, 1.5, 18.877501001),
        (2.5, 1.5, 12),
        (12.551689695, 1.5, 16.813717329),
        (10.538187101, 1.5, 19.484392155),
        (3.692636546, 1.5, 20.462327949),
        (-3.692636546, 1.5, -20.462327949),
        (-2.5, 1.5, -18.877501001),
        (-2.5, 1.5, -12),
        (-12.551689695, 1.5, -16.813717329),
        (-10.538187101, 1.5, -19.484392155),
    ]]
    fillet(fillet_6_edges, radius=FILLET_6_R)

    # 圆角7
    fillet_7_edges = [part.edges().sort_by_distance(p)[0] for p in [
        (-10.448310305, 1.5, 12.186282671),
        (-7.197224362, 1.5, 12),
        (10.448310305, 1.5, -12.186282671),
        (7.197224362, 1.5, -12),
        (7.197224362, 1.5, 12),
        (10.448310305, 1.5, 12.186282671),
        (-7.197224362, 1.5, -12),
        (-10.448310305, 1.5, -12.186282671),
    ]]
    fillet(fillet_7_edges, radius=FILLET_7_R)


solid = part.part
